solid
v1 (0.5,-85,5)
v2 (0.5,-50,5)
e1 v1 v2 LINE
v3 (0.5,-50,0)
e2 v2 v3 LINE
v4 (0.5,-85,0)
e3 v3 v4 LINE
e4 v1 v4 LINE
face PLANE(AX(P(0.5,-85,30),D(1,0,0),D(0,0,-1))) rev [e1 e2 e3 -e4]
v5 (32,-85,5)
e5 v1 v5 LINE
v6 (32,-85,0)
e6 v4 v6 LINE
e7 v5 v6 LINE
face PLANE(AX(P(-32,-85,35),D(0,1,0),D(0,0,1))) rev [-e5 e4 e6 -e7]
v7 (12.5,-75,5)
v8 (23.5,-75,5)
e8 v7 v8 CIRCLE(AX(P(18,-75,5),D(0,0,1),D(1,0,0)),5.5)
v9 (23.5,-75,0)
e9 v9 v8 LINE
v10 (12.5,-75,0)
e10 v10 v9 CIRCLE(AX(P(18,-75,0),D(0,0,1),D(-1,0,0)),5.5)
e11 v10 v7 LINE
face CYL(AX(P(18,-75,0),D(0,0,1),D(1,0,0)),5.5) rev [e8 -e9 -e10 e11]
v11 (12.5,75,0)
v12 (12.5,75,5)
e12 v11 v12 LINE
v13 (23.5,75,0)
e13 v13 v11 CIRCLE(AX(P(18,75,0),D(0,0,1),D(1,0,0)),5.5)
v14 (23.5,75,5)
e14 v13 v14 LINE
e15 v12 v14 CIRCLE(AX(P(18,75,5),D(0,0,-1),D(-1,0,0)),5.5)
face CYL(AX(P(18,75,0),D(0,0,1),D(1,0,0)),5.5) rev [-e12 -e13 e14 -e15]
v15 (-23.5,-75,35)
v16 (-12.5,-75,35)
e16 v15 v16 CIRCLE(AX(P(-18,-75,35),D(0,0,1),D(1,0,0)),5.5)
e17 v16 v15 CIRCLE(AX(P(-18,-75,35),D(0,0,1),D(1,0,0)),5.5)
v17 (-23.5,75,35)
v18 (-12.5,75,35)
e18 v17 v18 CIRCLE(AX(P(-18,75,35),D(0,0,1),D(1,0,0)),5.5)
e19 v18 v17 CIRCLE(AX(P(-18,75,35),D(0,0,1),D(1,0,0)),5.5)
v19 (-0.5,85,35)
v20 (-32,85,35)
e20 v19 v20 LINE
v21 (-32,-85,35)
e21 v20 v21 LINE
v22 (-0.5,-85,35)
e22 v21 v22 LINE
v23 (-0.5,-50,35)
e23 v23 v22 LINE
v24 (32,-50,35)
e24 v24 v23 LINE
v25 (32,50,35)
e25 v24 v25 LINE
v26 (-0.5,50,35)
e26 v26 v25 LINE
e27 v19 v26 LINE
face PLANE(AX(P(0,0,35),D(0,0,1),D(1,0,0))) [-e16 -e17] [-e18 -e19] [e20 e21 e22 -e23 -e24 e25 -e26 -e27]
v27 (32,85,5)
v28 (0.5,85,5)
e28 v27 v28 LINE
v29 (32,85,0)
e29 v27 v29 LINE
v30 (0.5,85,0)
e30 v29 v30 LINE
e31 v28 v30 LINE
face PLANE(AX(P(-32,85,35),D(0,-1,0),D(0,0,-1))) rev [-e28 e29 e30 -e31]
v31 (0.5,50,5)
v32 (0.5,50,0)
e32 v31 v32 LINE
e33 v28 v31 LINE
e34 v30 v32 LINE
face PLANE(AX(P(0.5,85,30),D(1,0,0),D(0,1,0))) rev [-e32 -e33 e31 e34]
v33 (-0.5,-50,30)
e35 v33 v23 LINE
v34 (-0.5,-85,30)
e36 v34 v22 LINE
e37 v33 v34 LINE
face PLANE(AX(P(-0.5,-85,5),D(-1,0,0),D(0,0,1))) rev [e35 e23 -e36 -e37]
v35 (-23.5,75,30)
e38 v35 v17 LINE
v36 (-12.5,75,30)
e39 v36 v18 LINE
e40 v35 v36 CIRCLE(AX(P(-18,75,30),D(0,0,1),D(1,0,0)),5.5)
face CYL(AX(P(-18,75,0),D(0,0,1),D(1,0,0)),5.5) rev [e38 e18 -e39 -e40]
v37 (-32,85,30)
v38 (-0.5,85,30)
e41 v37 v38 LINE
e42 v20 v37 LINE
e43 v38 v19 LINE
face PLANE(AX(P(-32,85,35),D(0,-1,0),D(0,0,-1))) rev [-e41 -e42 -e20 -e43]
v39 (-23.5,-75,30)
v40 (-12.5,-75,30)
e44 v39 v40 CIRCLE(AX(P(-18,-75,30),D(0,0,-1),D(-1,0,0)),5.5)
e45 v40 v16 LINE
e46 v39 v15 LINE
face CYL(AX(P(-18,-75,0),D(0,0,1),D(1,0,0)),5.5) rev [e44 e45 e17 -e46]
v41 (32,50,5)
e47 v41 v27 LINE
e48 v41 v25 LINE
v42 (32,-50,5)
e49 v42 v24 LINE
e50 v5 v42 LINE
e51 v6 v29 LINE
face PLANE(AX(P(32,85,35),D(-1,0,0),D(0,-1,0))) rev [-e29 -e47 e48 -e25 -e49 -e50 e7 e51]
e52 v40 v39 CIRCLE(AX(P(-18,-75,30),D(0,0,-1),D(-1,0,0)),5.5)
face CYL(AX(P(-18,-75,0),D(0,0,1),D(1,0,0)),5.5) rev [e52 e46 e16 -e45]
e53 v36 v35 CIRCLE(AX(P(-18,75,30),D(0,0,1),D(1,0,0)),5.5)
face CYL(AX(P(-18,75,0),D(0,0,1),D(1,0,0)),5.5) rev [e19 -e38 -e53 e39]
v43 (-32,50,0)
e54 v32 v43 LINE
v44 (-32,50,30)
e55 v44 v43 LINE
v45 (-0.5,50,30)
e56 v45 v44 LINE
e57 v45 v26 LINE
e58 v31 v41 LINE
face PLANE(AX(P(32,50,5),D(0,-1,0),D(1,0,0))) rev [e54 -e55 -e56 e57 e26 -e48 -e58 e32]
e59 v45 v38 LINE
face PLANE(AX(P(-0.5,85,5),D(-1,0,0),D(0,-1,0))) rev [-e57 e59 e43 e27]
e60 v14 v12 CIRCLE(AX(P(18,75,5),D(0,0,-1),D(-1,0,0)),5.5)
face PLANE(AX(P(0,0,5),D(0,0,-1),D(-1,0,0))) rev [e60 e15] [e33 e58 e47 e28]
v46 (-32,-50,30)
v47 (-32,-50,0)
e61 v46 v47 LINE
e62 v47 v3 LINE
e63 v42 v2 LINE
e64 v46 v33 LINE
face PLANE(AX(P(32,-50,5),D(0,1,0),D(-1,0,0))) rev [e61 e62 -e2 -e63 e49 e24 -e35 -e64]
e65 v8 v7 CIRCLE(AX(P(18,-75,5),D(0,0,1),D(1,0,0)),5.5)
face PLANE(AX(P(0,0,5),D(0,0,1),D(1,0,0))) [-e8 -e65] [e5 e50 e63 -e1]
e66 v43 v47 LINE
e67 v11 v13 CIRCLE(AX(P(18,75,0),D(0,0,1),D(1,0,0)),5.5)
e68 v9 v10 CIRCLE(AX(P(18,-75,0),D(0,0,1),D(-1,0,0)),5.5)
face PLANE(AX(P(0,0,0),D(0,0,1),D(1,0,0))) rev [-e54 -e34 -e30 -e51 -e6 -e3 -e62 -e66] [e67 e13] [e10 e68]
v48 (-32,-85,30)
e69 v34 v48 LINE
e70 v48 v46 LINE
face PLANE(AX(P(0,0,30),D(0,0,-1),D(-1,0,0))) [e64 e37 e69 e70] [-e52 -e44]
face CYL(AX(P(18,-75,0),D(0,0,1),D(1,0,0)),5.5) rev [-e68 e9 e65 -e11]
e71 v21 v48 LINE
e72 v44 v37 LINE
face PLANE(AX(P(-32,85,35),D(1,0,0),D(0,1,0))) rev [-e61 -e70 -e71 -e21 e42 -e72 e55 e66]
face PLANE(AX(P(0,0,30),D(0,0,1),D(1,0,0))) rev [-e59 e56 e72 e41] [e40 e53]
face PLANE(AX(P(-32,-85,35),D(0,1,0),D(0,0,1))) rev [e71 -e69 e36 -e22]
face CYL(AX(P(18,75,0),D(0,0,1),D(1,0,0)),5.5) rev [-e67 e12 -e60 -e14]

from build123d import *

# Parameters (mm, degrees)
SKETCH_1_W               = 64
SKETCH_1_H               = 170
EXTRUDE_1_DEPTH          = 35
SKETCH_3_W               = 32.5
SKETCH_3_H               = 35
CUT_EXTRUDE_1_DEPTH      = 30
SKETCH_4_W               = 32.5
SKETCH_4_H               = 35
CUT_EXTRUDE_2_DEPTH      = 30
CUT_EXTRUDE_3_DEPTH      = 98.334474879
CUT_EXTRUDE_3_DEPTH_BACK = 98.334474879
SKETCH_5_R               = 5.5


with BuildPart() as part:
    # 草图1 → 凸台-拉伸1 (new body)
    with BuildSketch(Plane.XY):
        Rectangle(SKETCH_1_W, SKETCH_1_H)
    extrude(amount=EXTRUDE_1_DEPTH)

    # 草图3 → 切除-拉伸1 (cut)
    with BuildSketch(Plane.XY.offset(35)):
        with Locations((15.75, 67.5)):
            Rectangle(SKETCH_3_W, SKETCH_3_H)
        with Locations((15.75, -67.5)):
            Rectangle(SKETCH_3_W, SKETCH_3_H)
    extrude(amount=-CUT_EXTRUDE_1_DEPTH, mode=Mode.SUBTRACT)

    # 草图4 → 切除-拉伸2 (cut)
    with BuildSketch(Plane(origin=(0, 0, 0), x_dir=(-1, 0, 0), z_dir=(0, 0, -1))):
        with Locations((15.75, 67.5)):
            Rectangle(SKETCH_4_W, SKETCH_4_H)
        with Locations((15.75, -67.5)):
            Rectangle(SKETCH_4_W, SKETCH_4_H)
    extrude(amount=-CUT_EXTRUDE_2_DEPTH, mode=Mode.SUBTRACT)

    # 草图5 → 切除-拉伸3 (cut, two sides: drawn at the far end of the back side and taken through both)
    with BuildSketch(Plane.XY.offset(35).offset(-CUT_EXTRUDE_3_DEPTH_BACK)):
        with Locations((-18, 75)):
            Circle(SKETCH_5_R)
        with Locations((18, 75)):
            Circle(SKETCH_5_R)
        with Locations((18, -75)):
            Circle(SKETCH_5_R)
        with Locations((-18, -75)):
            Circle(SKETCH_5_R)
    extrude(amount=CUT_EXTRUDE_3_DEPTH + CUT_EXTRUDE_3_DEPTH_BACK, mode=Mode.SUBTRACT)


solid = part.part
